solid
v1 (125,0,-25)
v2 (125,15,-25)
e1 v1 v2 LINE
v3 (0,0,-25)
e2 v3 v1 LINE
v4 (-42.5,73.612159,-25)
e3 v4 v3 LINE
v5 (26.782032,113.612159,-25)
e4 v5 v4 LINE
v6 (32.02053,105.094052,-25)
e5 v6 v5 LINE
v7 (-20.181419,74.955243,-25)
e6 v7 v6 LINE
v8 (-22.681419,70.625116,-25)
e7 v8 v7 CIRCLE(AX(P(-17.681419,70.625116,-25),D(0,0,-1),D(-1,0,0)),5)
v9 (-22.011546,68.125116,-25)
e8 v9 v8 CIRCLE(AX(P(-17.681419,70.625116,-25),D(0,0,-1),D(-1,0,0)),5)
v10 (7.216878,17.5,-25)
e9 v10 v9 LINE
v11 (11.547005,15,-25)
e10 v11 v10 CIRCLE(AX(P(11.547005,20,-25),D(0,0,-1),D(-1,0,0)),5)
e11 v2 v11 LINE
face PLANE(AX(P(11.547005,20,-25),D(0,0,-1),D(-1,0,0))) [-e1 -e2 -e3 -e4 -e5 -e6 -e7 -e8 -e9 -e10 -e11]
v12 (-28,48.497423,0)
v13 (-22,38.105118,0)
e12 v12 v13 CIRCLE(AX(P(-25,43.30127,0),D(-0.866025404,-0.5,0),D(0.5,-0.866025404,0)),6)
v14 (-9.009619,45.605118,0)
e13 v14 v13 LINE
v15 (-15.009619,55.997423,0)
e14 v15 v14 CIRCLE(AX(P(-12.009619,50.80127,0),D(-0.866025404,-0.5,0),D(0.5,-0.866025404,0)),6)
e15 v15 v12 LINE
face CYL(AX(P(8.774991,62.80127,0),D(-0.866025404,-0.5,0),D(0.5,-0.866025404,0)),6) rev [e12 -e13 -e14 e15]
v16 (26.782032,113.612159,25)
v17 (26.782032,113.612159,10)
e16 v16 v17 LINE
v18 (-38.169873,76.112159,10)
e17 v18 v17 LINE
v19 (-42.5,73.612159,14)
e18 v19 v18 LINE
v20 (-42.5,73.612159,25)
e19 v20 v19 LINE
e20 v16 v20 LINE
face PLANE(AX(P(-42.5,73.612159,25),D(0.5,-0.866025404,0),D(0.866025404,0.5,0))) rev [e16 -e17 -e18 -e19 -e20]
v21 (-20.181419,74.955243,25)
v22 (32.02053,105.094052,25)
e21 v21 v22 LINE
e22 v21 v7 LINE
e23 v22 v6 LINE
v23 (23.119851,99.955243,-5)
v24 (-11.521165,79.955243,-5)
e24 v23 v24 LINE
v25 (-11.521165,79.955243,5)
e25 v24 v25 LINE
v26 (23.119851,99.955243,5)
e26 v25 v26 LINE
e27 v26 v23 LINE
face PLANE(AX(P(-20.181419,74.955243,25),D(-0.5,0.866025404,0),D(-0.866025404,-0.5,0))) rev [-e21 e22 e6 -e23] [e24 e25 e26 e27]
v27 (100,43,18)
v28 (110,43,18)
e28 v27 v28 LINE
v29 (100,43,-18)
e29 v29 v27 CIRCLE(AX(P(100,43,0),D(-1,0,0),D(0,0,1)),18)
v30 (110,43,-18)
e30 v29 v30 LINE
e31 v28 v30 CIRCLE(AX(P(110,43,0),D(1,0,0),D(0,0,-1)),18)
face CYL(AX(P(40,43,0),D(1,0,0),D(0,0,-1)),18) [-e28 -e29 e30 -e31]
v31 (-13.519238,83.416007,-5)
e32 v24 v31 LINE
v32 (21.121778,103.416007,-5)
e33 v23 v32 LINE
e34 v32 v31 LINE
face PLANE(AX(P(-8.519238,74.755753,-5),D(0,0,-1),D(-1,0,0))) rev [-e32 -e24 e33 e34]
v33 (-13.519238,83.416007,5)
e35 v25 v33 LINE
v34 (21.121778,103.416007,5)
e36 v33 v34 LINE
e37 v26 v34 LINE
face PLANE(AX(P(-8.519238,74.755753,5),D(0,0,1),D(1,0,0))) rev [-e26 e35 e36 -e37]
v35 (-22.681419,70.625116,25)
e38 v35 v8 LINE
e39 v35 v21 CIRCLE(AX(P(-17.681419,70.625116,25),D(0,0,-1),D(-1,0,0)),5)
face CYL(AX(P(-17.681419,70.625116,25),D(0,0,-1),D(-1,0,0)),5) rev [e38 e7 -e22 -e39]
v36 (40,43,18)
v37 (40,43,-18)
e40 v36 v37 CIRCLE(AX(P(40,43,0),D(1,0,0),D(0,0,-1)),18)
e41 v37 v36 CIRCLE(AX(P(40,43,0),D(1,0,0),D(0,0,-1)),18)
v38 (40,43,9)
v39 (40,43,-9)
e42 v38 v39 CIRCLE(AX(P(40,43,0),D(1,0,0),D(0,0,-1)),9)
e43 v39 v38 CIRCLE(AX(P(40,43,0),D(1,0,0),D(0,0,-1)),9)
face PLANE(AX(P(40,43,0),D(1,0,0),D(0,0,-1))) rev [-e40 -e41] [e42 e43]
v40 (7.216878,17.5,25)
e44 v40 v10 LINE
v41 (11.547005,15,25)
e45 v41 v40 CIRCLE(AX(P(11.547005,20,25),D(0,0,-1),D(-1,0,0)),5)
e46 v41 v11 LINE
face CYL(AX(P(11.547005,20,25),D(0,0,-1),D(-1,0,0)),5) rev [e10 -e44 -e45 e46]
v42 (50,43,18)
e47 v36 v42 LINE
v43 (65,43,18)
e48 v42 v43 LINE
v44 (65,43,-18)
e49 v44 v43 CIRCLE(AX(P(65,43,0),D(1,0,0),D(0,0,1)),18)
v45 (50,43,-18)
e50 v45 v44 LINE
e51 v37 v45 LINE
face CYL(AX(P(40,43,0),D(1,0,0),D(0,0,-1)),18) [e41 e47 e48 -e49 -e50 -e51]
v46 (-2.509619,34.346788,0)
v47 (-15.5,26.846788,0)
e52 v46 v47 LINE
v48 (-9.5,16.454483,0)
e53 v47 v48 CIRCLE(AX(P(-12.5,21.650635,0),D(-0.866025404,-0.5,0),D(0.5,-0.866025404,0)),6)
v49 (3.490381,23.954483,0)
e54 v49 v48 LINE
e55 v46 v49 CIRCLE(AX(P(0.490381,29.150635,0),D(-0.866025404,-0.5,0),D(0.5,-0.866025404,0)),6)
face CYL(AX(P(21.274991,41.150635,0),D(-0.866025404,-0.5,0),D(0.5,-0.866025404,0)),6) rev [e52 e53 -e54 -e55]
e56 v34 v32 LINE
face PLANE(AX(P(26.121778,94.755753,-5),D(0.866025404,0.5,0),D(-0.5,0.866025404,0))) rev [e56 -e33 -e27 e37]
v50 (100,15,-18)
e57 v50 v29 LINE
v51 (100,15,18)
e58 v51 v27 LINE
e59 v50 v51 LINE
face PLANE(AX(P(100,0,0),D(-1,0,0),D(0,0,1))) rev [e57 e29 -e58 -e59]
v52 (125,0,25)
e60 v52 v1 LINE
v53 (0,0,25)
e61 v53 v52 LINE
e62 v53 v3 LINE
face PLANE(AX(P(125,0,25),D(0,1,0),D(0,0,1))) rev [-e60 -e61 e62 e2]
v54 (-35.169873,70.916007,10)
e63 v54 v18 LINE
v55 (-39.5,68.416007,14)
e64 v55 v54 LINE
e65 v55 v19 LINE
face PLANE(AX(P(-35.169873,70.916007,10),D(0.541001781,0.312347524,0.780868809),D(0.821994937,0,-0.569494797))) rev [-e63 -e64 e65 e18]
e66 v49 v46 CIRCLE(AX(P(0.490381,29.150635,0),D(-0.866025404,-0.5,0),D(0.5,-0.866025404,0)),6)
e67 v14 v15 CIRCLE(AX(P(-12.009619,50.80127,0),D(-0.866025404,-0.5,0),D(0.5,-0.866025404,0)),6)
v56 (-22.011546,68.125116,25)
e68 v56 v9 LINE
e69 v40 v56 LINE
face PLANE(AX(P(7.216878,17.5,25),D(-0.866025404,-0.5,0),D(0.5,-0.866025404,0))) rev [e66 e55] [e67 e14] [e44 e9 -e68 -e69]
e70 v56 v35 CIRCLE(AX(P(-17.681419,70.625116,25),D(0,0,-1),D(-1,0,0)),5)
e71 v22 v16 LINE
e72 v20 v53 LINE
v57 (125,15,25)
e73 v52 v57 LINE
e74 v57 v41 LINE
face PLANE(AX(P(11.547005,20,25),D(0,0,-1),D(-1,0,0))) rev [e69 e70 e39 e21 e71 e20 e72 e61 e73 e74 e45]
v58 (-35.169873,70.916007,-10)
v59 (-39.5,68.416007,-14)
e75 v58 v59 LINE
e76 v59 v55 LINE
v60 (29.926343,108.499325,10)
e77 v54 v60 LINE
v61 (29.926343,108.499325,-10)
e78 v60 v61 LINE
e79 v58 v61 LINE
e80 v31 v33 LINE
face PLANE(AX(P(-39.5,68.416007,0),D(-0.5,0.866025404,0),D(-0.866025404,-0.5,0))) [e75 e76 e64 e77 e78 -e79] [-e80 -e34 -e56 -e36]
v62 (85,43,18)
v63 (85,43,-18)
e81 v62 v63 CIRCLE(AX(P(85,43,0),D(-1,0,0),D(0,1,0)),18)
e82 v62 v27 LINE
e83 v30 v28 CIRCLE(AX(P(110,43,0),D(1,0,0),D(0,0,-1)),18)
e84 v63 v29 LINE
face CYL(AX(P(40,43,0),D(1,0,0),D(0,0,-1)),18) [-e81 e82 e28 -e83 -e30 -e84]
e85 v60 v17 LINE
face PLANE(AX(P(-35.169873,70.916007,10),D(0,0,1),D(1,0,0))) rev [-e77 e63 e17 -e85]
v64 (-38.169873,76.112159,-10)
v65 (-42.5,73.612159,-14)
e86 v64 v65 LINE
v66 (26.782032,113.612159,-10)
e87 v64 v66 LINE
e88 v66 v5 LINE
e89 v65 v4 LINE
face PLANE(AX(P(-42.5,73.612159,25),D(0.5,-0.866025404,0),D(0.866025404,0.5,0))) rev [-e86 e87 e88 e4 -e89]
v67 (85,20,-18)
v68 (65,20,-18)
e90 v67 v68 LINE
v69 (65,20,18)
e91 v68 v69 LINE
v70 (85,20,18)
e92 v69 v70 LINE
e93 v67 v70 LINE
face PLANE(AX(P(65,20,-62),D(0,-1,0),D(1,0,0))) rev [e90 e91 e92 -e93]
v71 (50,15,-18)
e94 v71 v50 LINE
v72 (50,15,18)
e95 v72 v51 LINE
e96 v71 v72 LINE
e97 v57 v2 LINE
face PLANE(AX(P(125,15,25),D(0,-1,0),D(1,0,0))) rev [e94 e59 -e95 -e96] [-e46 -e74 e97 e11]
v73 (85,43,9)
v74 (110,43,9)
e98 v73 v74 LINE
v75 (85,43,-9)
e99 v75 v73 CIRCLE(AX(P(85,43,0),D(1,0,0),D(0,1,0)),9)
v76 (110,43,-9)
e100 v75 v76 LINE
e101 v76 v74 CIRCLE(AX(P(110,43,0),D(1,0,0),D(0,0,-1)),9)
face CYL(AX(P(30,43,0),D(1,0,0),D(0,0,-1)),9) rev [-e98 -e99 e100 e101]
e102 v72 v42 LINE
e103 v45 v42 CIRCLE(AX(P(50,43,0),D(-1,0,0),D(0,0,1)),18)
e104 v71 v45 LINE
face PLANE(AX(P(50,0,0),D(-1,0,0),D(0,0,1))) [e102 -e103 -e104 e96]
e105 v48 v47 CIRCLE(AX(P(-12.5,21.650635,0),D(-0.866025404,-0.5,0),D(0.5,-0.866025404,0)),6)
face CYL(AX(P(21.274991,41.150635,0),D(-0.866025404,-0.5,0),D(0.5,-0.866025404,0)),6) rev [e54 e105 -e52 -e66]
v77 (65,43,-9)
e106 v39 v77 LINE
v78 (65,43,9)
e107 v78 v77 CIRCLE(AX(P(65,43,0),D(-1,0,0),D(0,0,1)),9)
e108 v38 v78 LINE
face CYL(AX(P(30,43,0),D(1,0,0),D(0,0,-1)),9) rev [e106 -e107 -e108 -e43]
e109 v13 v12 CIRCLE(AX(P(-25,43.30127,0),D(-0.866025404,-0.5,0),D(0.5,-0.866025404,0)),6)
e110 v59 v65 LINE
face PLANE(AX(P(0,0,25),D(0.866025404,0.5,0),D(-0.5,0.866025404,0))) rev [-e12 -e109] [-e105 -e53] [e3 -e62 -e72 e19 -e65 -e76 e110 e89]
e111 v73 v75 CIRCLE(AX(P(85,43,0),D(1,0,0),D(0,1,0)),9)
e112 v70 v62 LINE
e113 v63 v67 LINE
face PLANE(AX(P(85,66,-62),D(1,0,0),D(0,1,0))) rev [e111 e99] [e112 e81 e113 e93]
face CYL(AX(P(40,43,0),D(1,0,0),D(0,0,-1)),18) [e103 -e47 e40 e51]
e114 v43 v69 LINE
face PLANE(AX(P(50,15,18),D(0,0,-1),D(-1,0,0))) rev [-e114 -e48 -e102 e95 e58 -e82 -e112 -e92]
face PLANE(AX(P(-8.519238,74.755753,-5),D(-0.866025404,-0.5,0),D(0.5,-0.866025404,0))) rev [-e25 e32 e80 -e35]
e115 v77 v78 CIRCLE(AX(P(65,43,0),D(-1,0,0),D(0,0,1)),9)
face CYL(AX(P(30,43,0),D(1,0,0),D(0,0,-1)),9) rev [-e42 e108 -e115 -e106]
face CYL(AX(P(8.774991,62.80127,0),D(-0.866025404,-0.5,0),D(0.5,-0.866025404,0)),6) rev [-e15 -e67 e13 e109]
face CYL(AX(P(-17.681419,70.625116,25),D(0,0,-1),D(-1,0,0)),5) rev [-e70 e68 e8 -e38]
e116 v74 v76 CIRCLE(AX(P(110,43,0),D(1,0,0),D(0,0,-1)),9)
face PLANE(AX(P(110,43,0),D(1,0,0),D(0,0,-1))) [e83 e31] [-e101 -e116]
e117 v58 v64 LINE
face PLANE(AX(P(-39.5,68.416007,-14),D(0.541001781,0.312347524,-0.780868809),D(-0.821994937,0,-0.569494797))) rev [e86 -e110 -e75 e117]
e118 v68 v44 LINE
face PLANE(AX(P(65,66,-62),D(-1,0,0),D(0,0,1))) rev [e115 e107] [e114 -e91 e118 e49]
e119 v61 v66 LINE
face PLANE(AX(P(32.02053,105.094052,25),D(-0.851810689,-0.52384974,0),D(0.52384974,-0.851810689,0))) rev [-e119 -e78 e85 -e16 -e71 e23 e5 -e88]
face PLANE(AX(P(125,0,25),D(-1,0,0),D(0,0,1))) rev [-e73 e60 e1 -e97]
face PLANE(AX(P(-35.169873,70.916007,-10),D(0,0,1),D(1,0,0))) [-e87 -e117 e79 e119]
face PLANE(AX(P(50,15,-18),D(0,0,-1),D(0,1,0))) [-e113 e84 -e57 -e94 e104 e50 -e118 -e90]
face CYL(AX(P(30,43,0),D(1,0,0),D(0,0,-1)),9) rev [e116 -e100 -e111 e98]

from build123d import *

# Parameters (mm, degrees)
ANGLED_BRACKET_BODY_DEPTH  = 25
SLOT_20X5_SKETCH_W         = 83.357534166
SLOT_20X5_SKETCH_H         = 20
SLOT_CUT_20X5_DEPTH        = 6
POCKET_CUT_28X14_DEPTH     = 6
RECESS_40X10_SKETCH_W      = 40
RECESS_40X10_SKETCH_H      = 10
RECESS_CUT_40X10_DEPTH     = 10
CLEVIS_BLOCK_SKETCH_W      = 36
CLEVIS_BLOCK_SKETCH_H      = 28
CLEVIS_BLOCK_DEPTH         = 50
PIVOT_BOSSES_DEPTH         = 10
PIVOT_BOSSES_DEPTH_BACK    = 60
PIVOT_BOSS_SKETCH_R        = 18
CLEVIS_SLOT_SKETCH_W       = 20
CLEVIS_SLOT_SKETCH_H       = 46
CLEVIS_SLOT_20_WIDE_DEPTH  = 80
PIVOT_BORE_SKETCH_R        = 9
PIVOT_BORE_18_DEPTH        = 80
MOUNTING_HOLES_SKETCH_R    = 6
MOUNTING_HOLES_2X_12_DEPTH = 39


with BuildPart() as part:
    # Bracket Profile Sketch → Angled Bracket Body (new, symmetric)
    with BuildSketch(Plane.XY):
        with BuildLine():
            Line((125, 0), (0, 0))
            Line((0, 0), (-42.5, 73.612159322))
            Line((-42.5, 73.612159322), (26.782032303, 113.612159322))
            Line((26.782032303, 113.612159322), (32.020529704, 105.094052432))
            Line((32.020529704, 105.094052432), (-20.181419095, 74.955243241))
            ThreePointArc((-20.181419095, 74.955243241), (-22.511048226, 71.919211448), (-22.011546114, 68.125116222))
            Line((-22.011546114, 68.125116222), (7.216878365, 17.5))
            ThreePointArc((7.216878365, 17.5), (9.047005384, 15.669872981), (11.547005384, 15))
            Line((11.547005384, 15), (125, 15))
            Line((125, 15), (125, 0))
        make_face()
    extrude(amount=ANGLED_BRACKET_BODY_DEPTH, both=True)

    # Slot 20x5 Sketch → Slot Cut 20x5 (cut)
    with BuildSketch(Plane(origin=(-42.5, 73.612159322, 0), x_dir=(0.8660254037844364, 0.5000000000000041, 0), z_dir=(-0.5000000000000041, 0.8660254037844364, 0))):
        with Locations((46.678767083, 0)):
            Rectangle(SLOT_20X5_SKETCH_W, SLOT_20X5_SKETCH_H)
    extrude(amount=-SLOT_CUT_20X5_DEPTH, mode=Mode.SUBTRACT)

    # Pocket 28x14 Sketch → Pocket Cut 28x14 (cut)
    with BuildSketch(Plane(origin=(-42.5, 73.612159322, 0), x_dir=(0.8660254037844364, 0.5000000000000041, 0), z_dir=(-0.5000000000000041, 0.8660254037844364, 0))):
        Polygon((0, 14), (0, -14), (5, -10), (5, 10), align=None)
    extrude(amount=-POCKET_CUT_28X14_DEPTH, mode=Mode.SUBTRACT)

    # Recess 40x10 Sketch → Recess Cut 40x10 (cut)
    with BuildSketch(Plane(origin=(-39.5, 68.416006899, 0), x_dir=(0.8660254037844364, 0.5000000000000041, 0), z_dir=(-0.500000000000004, 0.8660254037844363, 0))):
        with Locations((50, 0)):
            Rectangle(RECESS_40X10_SKETCH_W, RECESS_40X10_SKETCH_H)
    extrude(amount=-RECESS_CUT_40X10_DEPTH, mode=Mode.SUBTRACT)

    # Clevis Block Sketch → Clevis Block (add)
    with BuildSketch(Plane(origin=(100, 0, 0), x_dir=(0, 0, -1), z_dir=(1, 0, 0))):
        with Locations((0, 29)):
            Rectangle(CLEVIS_BLOCK_SKETCH_W, CLEVIS_BLOCK_SKETCH_H)
    extrude(amount=-CLEVIS_BLOCK_DEPTH)

    # Pivot Boss Sketch → Pivot Bosses (add, two sides: drawn at the far end of the back side and taken through both)
    with BuildSketch(Plane(origin=(100, 0, 0), x_dir=(0, 0, -1), z_dir=(1, 0, 0)).offset(-PIVOT_BOSSES_DEPTH_BACK)):
        with Locations((0, 43)):
            Circle(PIVOT_BOSS_SKETCH_R)
    extrude(amount=PIVOT_BOSSES_DEPTH + PIVOT_BOSSES_DEPTH_BACK)

    # Clevis Slot Sketch → Clevis Slot 20 Wide (cut)
    with BuildSketch(Plane.XY.offset(18)):
        with Locations((75, 43)):
            Rectangle(CLEVIS_SLOT_SKETCH_W, CLEVIS_SLOT_SKETCH_H)
    extrude(amount=-CLEVIS_SLOT_20_WIDE_DEPTH, mode=Mode.SUBTRACT)

    # Pivot Bore Sketch → Pivot Bore Ø18 (cut)
    with BuildSketch(Plane(origin=(110, 0, 0), x_dir=(0, 0, -1), z_dir=(1, 0, 0))):
        with Locations((0, 43)):
            Circle(PIVOT_BORE_SKETCH_R)
    extrude(amount=-PIVOT_BORE_18_DEPTH, mode=Mode.SUBTRACT)

    # Mounting Holes Sketch → Mounting Holes 2xØ12 (cut)
    with BuildSketch(Plane(origin=(0, 0, 0), x_dir=(0, 0, 1), z_dir=(-0.8660254037844363, -0.5000000000000042, 0))):
        with Locations(Location((0, 50, 0), (0, 0, 270))):
            Circle(MOUNTING_HOLES_SKETCH_R)
        with Locations(Location((0, 25, 0), (0, 0, 270))):
            Circle(MOUNTING_HOLES_SKETCH_R)
    extrude(amount=-MOUNTING_HOLES_2X_12_DEPTH, mode=Mode.SUBTRACT)


solid = part.part
